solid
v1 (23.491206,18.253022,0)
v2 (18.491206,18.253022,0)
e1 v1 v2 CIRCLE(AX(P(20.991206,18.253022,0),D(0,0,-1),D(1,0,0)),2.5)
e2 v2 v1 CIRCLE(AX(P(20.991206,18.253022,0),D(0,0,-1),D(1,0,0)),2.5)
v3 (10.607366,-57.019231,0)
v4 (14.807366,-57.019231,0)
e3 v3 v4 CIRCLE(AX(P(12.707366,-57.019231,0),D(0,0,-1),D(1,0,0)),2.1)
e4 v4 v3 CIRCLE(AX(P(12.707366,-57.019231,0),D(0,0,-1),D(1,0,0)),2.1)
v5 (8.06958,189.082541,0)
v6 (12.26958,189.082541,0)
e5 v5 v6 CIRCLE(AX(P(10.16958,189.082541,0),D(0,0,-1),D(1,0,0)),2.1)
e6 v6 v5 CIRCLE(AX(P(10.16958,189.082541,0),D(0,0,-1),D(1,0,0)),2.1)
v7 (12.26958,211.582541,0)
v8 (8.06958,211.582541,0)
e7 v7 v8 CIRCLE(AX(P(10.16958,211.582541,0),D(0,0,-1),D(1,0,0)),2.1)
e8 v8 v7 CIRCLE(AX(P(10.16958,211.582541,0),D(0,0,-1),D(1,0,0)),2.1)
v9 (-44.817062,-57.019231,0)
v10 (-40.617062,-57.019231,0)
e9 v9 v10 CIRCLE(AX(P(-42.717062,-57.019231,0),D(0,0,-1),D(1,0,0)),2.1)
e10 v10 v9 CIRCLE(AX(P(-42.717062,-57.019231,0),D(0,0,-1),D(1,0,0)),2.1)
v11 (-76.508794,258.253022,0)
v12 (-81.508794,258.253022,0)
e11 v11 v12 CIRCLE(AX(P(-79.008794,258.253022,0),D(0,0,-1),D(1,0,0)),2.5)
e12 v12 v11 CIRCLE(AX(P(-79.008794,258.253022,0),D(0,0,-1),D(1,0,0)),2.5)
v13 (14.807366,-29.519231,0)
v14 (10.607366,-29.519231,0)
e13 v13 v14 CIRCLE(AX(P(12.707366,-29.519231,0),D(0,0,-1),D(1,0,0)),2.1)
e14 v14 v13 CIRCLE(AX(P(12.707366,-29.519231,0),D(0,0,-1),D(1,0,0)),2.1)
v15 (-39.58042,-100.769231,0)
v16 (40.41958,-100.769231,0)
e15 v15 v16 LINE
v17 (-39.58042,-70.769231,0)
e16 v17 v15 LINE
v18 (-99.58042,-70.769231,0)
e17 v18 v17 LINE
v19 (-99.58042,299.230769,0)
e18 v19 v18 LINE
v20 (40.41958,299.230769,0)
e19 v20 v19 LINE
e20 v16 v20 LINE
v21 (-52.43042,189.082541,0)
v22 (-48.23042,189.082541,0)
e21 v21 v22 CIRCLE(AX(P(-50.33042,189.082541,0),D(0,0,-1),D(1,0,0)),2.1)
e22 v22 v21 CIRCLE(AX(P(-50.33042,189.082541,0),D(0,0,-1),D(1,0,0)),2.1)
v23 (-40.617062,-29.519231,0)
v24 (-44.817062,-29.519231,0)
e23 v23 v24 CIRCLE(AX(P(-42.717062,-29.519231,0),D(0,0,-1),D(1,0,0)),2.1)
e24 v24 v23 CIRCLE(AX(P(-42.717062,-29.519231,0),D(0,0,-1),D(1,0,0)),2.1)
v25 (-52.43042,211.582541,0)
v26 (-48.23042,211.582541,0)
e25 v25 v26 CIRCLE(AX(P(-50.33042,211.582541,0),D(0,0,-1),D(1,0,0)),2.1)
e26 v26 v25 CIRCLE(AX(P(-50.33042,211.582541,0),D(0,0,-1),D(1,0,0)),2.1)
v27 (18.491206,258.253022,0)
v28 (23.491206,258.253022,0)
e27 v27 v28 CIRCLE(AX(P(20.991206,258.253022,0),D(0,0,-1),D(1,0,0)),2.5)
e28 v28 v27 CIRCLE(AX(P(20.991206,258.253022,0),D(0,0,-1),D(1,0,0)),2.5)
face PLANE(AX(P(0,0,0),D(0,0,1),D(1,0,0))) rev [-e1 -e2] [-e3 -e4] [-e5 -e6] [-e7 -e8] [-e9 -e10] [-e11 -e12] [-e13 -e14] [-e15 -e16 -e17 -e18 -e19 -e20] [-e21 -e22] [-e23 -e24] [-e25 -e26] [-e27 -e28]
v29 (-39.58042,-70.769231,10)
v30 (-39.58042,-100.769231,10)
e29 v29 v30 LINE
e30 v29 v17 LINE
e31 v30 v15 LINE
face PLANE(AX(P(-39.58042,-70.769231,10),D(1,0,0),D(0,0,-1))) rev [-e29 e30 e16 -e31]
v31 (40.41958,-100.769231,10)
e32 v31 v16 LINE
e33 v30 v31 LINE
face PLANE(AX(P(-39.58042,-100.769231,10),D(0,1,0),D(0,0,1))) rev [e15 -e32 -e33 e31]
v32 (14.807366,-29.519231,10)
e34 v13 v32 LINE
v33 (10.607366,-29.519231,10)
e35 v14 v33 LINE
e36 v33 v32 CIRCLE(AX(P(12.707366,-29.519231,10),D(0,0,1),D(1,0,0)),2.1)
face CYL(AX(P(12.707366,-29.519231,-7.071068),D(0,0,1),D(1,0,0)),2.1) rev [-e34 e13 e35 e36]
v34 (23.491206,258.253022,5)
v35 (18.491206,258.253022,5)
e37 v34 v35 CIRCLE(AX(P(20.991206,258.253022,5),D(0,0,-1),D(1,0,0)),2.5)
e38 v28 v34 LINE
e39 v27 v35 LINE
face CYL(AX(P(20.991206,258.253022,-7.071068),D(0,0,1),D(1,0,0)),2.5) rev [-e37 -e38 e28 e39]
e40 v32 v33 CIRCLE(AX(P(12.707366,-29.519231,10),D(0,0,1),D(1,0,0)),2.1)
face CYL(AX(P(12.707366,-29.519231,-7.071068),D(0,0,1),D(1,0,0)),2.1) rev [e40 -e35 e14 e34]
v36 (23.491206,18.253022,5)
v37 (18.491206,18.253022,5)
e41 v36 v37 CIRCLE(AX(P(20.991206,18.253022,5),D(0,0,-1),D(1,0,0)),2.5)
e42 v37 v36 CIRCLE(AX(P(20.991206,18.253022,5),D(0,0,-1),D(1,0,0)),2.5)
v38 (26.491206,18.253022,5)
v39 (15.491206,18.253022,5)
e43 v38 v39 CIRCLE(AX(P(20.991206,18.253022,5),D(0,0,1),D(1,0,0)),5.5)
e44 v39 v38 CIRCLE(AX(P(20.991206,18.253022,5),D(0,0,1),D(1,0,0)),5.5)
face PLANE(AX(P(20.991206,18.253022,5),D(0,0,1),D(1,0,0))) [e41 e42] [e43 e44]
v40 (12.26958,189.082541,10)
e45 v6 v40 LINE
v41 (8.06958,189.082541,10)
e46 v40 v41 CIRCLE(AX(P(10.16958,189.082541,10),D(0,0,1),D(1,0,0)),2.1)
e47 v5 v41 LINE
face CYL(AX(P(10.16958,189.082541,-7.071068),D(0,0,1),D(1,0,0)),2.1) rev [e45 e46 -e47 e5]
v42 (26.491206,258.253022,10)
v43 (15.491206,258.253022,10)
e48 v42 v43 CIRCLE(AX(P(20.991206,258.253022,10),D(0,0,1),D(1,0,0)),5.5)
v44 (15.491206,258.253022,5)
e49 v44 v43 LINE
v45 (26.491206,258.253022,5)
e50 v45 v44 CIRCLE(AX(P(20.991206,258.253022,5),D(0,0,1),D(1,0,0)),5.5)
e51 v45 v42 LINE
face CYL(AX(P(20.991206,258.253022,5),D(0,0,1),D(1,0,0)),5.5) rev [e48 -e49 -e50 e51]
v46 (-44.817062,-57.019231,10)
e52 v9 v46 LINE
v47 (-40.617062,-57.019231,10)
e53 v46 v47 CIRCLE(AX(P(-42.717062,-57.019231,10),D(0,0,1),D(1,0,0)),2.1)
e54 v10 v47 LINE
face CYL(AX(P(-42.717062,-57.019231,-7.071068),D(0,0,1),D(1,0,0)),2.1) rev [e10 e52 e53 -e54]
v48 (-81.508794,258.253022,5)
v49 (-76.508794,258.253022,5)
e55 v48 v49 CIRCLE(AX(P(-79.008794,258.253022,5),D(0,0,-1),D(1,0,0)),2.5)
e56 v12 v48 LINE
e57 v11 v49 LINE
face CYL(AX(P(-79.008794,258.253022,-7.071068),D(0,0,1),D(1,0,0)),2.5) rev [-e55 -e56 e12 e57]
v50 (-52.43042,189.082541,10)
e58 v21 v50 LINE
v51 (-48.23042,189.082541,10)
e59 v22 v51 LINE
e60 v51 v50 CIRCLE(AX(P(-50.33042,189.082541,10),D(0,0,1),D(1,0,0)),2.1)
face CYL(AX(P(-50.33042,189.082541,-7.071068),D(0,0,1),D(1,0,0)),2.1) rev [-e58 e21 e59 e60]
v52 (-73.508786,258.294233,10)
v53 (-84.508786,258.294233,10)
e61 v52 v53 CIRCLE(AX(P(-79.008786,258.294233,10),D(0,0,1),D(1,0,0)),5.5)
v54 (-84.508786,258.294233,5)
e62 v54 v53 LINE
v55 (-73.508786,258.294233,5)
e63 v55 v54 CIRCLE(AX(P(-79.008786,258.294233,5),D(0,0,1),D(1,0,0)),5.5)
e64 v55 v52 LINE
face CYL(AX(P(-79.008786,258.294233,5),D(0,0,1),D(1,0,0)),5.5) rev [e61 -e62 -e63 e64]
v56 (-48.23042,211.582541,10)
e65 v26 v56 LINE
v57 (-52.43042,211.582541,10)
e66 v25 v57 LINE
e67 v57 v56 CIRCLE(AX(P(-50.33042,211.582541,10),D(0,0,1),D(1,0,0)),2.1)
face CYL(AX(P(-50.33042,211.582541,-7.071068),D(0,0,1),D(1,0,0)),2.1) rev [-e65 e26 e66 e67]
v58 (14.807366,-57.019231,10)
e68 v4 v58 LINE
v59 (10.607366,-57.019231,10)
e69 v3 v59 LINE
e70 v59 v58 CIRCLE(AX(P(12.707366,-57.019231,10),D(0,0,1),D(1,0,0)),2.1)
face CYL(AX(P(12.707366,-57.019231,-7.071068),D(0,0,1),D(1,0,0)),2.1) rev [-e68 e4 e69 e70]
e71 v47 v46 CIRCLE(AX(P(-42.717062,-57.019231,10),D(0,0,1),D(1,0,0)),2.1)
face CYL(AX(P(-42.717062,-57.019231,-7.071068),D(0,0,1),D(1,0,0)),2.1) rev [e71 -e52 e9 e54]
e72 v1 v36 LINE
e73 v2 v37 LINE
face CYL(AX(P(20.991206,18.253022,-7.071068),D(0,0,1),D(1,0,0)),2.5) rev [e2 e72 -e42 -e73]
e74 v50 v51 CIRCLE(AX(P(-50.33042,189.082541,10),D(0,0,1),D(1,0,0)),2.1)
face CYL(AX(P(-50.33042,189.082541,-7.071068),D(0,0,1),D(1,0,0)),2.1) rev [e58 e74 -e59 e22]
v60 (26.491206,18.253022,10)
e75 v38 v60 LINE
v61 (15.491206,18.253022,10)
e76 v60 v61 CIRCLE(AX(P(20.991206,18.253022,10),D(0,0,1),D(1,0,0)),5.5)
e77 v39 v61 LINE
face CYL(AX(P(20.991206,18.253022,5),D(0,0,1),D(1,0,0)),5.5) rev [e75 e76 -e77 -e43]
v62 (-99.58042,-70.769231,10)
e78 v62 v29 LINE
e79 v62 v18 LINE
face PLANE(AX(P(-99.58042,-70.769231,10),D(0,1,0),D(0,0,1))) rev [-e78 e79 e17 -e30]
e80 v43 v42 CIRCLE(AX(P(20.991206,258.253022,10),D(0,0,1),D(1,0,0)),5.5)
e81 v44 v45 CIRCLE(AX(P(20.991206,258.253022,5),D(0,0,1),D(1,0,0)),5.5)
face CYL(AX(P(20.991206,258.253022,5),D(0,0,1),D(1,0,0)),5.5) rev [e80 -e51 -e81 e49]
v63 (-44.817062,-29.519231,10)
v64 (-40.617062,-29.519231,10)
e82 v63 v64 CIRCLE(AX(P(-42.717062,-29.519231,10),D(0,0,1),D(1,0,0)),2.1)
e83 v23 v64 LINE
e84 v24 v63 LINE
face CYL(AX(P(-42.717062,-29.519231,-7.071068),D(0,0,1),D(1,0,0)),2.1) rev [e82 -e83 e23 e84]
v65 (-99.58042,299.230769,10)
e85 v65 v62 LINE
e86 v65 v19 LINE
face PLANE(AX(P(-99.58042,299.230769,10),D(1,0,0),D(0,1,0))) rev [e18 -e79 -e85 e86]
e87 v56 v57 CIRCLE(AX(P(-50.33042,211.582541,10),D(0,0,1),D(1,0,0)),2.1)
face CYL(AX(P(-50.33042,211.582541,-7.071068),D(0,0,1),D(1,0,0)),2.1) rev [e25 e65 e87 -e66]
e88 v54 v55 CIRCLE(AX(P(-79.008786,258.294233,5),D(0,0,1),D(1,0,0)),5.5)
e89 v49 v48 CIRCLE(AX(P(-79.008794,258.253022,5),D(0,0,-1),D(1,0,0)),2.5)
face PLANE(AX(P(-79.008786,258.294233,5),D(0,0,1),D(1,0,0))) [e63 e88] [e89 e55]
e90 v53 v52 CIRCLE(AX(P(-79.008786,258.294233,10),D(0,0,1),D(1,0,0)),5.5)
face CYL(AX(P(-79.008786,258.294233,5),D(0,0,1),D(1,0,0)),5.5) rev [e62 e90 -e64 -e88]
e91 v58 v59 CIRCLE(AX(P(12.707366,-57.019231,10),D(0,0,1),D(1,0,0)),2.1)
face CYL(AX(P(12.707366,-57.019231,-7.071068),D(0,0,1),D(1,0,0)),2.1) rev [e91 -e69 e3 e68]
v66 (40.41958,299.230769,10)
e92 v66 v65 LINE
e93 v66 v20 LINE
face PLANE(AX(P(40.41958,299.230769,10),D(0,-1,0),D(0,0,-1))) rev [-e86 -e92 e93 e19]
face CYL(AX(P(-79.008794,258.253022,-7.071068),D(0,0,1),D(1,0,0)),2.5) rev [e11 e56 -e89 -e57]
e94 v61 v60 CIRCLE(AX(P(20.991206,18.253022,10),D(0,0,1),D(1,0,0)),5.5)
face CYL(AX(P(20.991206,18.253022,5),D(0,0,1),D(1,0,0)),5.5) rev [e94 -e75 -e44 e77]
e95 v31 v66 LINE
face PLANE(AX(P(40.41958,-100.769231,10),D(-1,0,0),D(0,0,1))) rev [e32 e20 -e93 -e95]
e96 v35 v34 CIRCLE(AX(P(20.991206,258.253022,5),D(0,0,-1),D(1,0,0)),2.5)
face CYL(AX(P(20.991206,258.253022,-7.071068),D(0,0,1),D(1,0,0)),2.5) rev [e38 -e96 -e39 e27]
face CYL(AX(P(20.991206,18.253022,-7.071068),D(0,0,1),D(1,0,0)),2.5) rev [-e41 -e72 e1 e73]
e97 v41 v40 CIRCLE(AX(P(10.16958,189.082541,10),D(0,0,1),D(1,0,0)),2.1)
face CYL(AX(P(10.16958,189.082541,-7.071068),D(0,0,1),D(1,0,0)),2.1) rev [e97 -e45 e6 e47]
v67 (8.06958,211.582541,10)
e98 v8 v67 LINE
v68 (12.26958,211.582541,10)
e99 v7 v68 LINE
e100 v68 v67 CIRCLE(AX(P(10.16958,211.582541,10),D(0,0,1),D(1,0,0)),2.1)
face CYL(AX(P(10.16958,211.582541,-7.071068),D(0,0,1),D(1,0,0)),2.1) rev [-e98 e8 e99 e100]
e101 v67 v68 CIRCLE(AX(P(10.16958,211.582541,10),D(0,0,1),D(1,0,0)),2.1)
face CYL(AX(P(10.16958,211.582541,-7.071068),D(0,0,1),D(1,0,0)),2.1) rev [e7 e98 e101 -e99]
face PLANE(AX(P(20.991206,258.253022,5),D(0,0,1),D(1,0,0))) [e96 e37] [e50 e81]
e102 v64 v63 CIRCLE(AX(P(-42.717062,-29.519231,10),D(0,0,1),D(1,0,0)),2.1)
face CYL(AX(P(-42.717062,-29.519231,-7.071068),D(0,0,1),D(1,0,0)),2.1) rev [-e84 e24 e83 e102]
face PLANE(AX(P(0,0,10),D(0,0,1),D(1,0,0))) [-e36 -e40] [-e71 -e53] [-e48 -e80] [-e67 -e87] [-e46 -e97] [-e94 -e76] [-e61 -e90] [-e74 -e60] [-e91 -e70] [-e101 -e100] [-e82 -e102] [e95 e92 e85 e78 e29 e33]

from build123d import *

# Parameters (mm, degrees)
EXTRUDE_1_DEPTH     = 10
SKETCH_10_R         = 2.5
SKETCH_10_R_2       = 2.1
CUT_EXTRUDE_1_DEPTH = 10
SKETCH_11_R         = 5.5
CUT_EXTRUDE_2_DEPTH = 5


with BuildPart() as part:
    # 草图1 → 凸台-拉伸1 (new body)
    with BuildSketch(Plane.XY):
        Polygon((-99.58041958, -70.769230769), (-39.58041958, -70.769230769), (-39.58041958, -100.769230769), (40.41958042, -100.769230769), (40.41958042, 299.230769231), (-99.58041958, 299.230769231), align=None)
    extrude(amount=EXTRUDE_1_DEPTH)

    # 草图10 → 切除-拉伸1 (cut)
    with BuildSketch(Plane.XY.offset(10)):
        with Locations((-79.008794304, 258.253022412)):
            Circle(SKETCH_10_R)
        with Locations((20.991205696, 258.253022412)):
            Circle(SKETCH_10_R)
        with Locations((-50.330419577, 211.582541175)):
            Circle(SKETCH_10_R_2)
        with Locations((-50.330419577, 189.082541175)):
            Circle(SKETCH_10_R_2)
        with Locations((10.169580423, 211.582541175)):
            Circle(SKETCH_10_R_2)
        with Locations((10.169580423, 189.082541175)):
            Circle(SKETCH_10_R_2)
        with Locations((-42.717061736, -29.519230769)):
            Circle(SKETCH_10_R_2)
        with Locations((-42.717061736, -57.019230769)):
            Circle(SKETCH_10_R_2)
        with Locations((12.707366369, -57.019230769)):
            Circle(SKETCH_10_R_2)
        with Locations((12.707366369, -29.519230769)):
            Circle(SKETCH_10_R_2)
        with Locations((20.991205696, 18.253022412)):
            Circle(SKETCH_10_R)
    extrude(amount=-CUT_EXTRUDE_1_DEPTH, mode=Mode.SUBTRACT)

    # 草图11 → 切除-拉伸2 (cut)
    with BuildSketch(Plane(origin=(-949.724352481, 990.975018952, 10), x_dir=(0, -1, 0), z_dir=(0, 0, 1))):
        with Locations(Location((732.680785462, 870.715566681, 0), (0, 0, 90))):
            Circle(SKETCH_11_R)
        with Locations(Location((732.72199654, 970.71555819, 0), (0, 0, 90))):
            Circle(SKETCH_11_R)
        with Locations(Location((972.72199654, 970.71555819, 0), (0, 0, 90))):
            Circle(SKETCH_11_R)
    extrude(amount=-CUT_EXTRUDE_2_DEPTH, mode=Mode.SUBTRACT)


solid = part.part
